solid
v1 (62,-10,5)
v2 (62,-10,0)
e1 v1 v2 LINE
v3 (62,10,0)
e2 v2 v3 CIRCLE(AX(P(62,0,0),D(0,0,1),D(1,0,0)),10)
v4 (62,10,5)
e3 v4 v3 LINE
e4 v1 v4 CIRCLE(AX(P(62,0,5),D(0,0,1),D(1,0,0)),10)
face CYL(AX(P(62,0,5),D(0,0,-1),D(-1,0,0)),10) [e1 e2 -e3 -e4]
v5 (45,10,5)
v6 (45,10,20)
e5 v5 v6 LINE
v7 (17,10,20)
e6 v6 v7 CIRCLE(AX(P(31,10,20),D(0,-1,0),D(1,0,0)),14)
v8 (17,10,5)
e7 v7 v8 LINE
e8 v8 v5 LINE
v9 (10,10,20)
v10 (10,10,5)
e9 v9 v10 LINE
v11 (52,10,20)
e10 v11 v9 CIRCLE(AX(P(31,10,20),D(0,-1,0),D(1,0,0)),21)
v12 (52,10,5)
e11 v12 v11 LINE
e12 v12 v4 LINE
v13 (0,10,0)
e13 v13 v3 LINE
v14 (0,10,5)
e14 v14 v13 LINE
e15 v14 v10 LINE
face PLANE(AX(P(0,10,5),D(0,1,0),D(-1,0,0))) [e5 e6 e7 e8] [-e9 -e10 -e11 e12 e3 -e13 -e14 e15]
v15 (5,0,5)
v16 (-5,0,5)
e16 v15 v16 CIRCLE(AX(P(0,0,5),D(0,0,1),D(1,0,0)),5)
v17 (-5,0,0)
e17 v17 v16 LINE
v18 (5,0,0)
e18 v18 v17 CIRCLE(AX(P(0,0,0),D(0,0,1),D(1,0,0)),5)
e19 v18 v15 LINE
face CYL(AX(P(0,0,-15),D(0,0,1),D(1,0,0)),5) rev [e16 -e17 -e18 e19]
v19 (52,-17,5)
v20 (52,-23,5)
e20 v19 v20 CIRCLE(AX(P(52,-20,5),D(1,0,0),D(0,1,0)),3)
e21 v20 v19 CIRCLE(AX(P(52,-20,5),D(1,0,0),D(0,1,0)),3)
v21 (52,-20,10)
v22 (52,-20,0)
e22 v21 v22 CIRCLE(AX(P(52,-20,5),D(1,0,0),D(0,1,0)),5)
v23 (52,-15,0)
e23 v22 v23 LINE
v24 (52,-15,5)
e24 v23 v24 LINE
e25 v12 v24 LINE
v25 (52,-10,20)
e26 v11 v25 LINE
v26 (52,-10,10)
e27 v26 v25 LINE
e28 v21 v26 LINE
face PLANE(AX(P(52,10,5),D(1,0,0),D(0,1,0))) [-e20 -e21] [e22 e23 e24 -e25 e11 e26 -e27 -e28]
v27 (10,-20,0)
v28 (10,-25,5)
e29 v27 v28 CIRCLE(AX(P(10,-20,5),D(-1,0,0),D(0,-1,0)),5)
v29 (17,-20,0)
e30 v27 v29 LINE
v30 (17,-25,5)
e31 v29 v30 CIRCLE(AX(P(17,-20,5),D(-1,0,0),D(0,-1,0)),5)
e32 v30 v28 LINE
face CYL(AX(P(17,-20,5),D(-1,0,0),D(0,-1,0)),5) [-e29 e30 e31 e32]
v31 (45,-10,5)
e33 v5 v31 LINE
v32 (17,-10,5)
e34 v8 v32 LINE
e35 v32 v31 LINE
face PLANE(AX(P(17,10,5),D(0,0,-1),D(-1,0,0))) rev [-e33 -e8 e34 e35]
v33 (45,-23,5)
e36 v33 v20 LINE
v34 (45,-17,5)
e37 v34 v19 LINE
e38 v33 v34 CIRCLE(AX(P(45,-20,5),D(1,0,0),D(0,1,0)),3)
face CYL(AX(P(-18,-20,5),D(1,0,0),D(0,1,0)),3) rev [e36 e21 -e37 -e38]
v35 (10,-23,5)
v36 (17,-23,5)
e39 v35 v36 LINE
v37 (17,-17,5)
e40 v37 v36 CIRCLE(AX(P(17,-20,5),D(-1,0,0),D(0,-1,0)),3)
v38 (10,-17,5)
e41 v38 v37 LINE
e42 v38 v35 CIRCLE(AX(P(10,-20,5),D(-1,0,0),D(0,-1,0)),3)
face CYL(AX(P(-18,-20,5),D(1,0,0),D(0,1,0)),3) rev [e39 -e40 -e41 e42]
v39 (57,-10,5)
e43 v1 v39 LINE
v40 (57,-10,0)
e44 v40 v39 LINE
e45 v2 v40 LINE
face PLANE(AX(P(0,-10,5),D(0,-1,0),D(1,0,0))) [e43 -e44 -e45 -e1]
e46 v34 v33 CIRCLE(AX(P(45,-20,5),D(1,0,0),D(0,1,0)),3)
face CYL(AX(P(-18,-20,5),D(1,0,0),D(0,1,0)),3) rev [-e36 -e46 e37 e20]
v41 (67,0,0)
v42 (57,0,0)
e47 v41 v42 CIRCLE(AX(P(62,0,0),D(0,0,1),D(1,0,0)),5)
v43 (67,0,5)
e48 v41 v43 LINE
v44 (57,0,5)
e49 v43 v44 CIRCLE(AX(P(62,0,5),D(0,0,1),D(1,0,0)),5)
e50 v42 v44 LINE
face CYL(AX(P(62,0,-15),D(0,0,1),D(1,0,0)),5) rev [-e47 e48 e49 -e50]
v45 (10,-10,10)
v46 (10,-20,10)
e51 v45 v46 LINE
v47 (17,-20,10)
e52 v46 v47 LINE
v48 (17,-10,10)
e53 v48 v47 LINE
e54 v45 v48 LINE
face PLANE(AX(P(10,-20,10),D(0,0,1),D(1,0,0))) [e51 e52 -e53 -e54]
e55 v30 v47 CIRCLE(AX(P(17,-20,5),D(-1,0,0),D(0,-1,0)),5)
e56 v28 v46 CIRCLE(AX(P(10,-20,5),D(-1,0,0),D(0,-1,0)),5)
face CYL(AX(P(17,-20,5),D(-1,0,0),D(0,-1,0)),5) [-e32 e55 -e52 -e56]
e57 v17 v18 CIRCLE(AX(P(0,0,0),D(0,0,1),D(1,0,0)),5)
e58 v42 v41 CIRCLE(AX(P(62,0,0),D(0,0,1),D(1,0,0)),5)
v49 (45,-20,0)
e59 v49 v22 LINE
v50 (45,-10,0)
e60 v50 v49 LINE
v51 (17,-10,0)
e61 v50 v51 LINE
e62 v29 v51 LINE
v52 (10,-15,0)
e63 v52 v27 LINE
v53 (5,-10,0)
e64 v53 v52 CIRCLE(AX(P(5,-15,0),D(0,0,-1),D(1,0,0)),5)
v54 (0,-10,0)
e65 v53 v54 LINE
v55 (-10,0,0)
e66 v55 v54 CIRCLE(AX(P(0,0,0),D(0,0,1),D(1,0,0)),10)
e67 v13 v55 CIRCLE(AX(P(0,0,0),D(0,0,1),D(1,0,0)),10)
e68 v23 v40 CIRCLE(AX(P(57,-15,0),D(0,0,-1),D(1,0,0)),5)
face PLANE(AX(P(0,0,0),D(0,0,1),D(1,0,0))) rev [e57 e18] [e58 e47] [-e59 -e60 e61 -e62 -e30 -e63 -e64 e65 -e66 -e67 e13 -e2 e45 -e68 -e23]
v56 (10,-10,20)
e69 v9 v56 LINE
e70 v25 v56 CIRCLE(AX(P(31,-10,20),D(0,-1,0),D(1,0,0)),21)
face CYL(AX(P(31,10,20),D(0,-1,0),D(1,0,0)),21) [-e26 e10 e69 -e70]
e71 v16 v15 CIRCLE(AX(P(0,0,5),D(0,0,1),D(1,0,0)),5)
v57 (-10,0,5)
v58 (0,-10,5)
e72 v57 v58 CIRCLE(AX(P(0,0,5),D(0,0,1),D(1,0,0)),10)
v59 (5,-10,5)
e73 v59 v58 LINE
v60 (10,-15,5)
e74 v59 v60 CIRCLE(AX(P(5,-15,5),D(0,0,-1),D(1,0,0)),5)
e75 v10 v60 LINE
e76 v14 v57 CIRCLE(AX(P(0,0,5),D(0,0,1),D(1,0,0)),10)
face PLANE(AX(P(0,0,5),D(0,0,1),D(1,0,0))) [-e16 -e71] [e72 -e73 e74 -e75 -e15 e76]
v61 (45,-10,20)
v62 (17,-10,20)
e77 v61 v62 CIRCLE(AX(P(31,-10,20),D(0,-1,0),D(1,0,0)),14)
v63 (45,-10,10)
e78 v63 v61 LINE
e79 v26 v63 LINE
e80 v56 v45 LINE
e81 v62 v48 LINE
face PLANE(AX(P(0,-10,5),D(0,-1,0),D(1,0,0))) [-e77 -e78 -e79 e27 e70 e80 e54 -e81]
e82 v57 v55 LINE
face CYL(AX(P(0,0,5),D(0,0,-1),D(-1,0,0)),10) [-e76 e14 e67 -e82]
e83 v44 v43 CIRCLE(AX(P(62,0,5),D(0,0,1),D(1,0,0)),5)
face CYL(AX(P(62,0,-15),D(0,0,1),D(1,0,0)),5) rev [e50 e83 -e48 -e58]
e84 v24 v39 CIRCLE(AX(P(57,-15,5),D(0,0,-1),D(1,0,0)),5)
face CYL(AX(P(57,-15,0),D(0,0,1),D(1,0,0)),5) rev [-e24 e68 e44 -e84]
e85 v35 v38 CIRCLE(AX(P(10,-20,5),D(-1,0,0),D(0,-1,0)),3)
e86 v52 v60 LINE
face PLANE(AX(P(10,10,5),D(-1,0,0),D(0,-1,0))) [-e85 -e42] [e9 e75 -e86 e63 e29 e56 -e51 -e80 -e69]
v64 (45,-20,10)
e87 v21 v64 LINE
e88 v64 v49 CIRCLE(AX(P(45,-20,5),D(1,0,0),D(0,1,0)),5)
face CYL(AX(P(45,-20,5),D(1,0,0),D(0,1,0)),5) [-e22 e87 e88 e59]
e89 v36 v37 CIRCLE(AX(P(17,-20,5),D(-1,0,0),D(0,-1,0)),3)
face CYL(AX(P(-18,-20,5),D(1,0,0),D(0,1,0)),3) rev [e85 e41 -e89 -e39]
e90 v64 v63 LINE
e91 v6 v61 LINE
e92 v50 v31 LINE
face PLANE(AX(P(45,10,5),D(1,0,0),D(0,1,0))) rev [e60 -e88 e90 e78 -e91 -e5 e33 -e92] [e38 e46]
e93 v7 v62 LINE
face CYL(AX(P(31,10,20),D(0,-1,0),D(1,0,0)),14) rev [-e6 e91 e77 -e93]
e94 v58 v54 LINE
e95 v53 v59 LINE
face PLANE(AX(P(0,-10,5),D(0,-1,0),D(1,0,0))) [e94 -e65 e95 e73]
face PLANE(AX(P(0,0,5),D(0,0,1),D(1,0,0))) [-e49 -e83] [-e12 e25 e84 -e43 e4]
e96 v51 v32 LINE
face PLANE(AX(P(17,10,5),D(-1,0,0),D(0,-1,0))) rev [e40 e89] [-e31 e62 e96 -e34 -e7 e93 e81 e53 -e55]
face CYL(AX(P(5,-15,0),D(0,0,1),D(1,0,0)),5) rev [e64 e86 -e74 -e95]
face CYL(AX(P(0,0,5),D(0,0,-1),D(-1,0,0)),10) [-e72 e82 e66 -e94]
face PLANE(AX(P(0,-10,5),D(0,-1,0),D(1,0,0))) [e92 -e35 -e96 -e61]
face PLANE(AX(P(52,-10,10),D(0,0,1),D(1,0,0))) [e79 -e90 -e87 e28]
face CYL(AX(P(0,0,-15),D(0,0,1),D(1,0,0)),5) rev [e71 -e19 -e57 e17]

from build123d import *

# Parameters (mm, degrees)
BASE_FLANGE_DEPTH        = 5
CLAMP_BODY_DEPTH         = 20
BORE_28_DEPTH            = 20
FLANGE_CUT_SKETCH_R      = 5
FLANGE_CUT_DEPTH         = 20
LUG_A_DEPTH              = 5
LUG_A_WEB_SKETCH_W       = 5
LUG_A_WEB_SKETCH_H       = 10
LUG_A_WEB_DEPTH          = 7
LUG_B_DEPTH              = 5
LUG_BRIDGE_SKETCH_W      = 5
LUG_BRIDGE_SKETCH_H      = 10
LUG_BRIDGE_DEPTH         = 7
EAR_A_DEPTH              = 7
EAR_START                = -7
EAR_B_DEPTH              = 7
CLAMP_BOLT_HOLE_SKETCH_R = 3
CLAMP_BOLT_HOLE_6_DEPTH  = 70


with BuildPart() as part:
    # Base Flange Sketch → Base Flange (new body)
    with BuildSketch(Plane.XY):
        with BuildLine():
            Line((62, -10), (0, -10))
            ThreePointArc((0, -10), (-10, 0), (0, 10))
            Line((0, 10), (62, 10))
            ThreePointArc((62, 10), (72, 0), (62, -10))
        make_face()
    extrude(amount=BASE_FLANGE_DEPTH)

    # Clamp Body Sketch → Clamp Body (add)
    with BuildSketch(Plane.XZ.offset(10)):
        with BuildLine():
            Line((10, 5), (52, 5))
            Line((52, 5), (52, 20))
            ThreePointArc((52, 20), (31, 41), (10, 20))
            Line((10, 20), (10, 5))
        make_face()
    extrude(amount=-CLAMP_BODY_DEPTH)

    # Bore Sketch → Bore Ø28 (cut)
    with BuildSketch(Plane.XZ.offset(10)):
        with BuildLine():
            Line((17, 5), (17, 20))
            ThreePointArc((17, 20), (31, 34), (45, 20))
            Line((45, 20), (45, 5))
            Line((45, 5), (17, 5))
        make_face()
    extrude(amount=-BORE_28_DEPTH, mode=Mode.SUBTRACT)

    # Flange Cut Sketch → Flange Cut (cut)
    with BuildSketch(Plane.XY.offset(5)):
        with Locations((62, 0)):
            Circle(FLANGE_CUT_SKETCH_R)
        Circle(FLANGE_CUT_SKETCH_R)
    extrude(amount=-FLANGE_CUT_DEPTH, mode=Mode.SUBTRACT)

    # Lug A Sketch → Lug A (add)
    with BuildSketch(Plane.XY.offset(5)):
        with BuildLine():
            Line((10, -10), (5, -10))
            ThreePointArc((5, -10), (8.535533906, -11.464466094), (10, -15))
            Line((10, -15), (10, -20))
            Line((10, -20), (17, -20))
            Line((17, -20), (17, -10))
            Line((17, -10), (10, -10))
        make_face()
    extrude(amount=-LUG_A_DEPTH)

    # Lug A Web Sketch → Lug A Web (add)
    with BuildSketch(Plane(origin=(17, 0, 0), x_dir=(0, 0, -1), z_dir=(1, 0, 0))):
        with Locations((-7.5, -15)):
            Rectangle(LUG_A_WEB_SKETCH_W, LUG_A_WEB_SKETCH_H)
    extrude(amount=-LUG_A_WEB_DEPTH)

    # Lug B Sketch → Lug B (add)
    with BuildSketch(Plane.XY.offset(5)):
        with BuildLine():
            Line((52, -10), (57, -10))
            ThreePointArc((57, -10), (53.464466094, -11.464466094), (52, -15))
            Line((52, -15), (52, -20))
            Line((52, -20), (45, -20))
            Line((45, -20), (45, -10))
            Line((45, -10), (52, -10))
        make_face()
    extrude(amount=-LUG_B_DEPTH)

    # Lug Bridge Sketch → Lug Bridge (add)
    with BuildSketch(Plane.ZY.offset(-45)):
        with Locations((7.5, -15)):
            Rectangle(LUG_BRIDGE_SKETCH_W, LUG_BRIDGE_SKETCH_H)
    extrude(amount=-LUG_BRIDGE_DEPTH)

    # Ear A Sketch → Ear A (add)
    with BuildSketch(Plane.ZY.offset(-10)):
        with BuildLine():
            Line((0, -20), (10, -20))
            ThreePointArc((10, -20), (5, -25), (0, -20))
        make_face()
    extrude(amount=-EAR_A_DEPTH)

    # Ear B Sketch → Ear B (add)
    with BuildSketch(Plane(origin=(52, 0, 0), x_dir=(0, 0, -1), z_dir=(1, 0, 0)).offset(EAR_START)):
        with BuildLine():
            Line((-10, -20), (0, -20))
            ThreePointArc((0, -20), (-5, -25), (-10, -20))
        make_face()
    extrude(amount=EAR_B_DEPTH)

    # Clamp Bolt Hole Sketch → Clamp Bolt Hole Ø6 (cut)
    with BuildSketch(Plane(origin=(52, 0, 0), x_dir=(0, 0, -1), z_dir=(1, 0, 0))):
        with Locations(Location((-5, -20, 0), (0, 0, 90))):
            Circle(CLAMP_BOLT_HOLE_SKETCH_R)
    extrude(amount=-CLAMP_BOLT_HOLE_6_DEPTH, mode=Mode.SUBTRACT)


solid = part.part
